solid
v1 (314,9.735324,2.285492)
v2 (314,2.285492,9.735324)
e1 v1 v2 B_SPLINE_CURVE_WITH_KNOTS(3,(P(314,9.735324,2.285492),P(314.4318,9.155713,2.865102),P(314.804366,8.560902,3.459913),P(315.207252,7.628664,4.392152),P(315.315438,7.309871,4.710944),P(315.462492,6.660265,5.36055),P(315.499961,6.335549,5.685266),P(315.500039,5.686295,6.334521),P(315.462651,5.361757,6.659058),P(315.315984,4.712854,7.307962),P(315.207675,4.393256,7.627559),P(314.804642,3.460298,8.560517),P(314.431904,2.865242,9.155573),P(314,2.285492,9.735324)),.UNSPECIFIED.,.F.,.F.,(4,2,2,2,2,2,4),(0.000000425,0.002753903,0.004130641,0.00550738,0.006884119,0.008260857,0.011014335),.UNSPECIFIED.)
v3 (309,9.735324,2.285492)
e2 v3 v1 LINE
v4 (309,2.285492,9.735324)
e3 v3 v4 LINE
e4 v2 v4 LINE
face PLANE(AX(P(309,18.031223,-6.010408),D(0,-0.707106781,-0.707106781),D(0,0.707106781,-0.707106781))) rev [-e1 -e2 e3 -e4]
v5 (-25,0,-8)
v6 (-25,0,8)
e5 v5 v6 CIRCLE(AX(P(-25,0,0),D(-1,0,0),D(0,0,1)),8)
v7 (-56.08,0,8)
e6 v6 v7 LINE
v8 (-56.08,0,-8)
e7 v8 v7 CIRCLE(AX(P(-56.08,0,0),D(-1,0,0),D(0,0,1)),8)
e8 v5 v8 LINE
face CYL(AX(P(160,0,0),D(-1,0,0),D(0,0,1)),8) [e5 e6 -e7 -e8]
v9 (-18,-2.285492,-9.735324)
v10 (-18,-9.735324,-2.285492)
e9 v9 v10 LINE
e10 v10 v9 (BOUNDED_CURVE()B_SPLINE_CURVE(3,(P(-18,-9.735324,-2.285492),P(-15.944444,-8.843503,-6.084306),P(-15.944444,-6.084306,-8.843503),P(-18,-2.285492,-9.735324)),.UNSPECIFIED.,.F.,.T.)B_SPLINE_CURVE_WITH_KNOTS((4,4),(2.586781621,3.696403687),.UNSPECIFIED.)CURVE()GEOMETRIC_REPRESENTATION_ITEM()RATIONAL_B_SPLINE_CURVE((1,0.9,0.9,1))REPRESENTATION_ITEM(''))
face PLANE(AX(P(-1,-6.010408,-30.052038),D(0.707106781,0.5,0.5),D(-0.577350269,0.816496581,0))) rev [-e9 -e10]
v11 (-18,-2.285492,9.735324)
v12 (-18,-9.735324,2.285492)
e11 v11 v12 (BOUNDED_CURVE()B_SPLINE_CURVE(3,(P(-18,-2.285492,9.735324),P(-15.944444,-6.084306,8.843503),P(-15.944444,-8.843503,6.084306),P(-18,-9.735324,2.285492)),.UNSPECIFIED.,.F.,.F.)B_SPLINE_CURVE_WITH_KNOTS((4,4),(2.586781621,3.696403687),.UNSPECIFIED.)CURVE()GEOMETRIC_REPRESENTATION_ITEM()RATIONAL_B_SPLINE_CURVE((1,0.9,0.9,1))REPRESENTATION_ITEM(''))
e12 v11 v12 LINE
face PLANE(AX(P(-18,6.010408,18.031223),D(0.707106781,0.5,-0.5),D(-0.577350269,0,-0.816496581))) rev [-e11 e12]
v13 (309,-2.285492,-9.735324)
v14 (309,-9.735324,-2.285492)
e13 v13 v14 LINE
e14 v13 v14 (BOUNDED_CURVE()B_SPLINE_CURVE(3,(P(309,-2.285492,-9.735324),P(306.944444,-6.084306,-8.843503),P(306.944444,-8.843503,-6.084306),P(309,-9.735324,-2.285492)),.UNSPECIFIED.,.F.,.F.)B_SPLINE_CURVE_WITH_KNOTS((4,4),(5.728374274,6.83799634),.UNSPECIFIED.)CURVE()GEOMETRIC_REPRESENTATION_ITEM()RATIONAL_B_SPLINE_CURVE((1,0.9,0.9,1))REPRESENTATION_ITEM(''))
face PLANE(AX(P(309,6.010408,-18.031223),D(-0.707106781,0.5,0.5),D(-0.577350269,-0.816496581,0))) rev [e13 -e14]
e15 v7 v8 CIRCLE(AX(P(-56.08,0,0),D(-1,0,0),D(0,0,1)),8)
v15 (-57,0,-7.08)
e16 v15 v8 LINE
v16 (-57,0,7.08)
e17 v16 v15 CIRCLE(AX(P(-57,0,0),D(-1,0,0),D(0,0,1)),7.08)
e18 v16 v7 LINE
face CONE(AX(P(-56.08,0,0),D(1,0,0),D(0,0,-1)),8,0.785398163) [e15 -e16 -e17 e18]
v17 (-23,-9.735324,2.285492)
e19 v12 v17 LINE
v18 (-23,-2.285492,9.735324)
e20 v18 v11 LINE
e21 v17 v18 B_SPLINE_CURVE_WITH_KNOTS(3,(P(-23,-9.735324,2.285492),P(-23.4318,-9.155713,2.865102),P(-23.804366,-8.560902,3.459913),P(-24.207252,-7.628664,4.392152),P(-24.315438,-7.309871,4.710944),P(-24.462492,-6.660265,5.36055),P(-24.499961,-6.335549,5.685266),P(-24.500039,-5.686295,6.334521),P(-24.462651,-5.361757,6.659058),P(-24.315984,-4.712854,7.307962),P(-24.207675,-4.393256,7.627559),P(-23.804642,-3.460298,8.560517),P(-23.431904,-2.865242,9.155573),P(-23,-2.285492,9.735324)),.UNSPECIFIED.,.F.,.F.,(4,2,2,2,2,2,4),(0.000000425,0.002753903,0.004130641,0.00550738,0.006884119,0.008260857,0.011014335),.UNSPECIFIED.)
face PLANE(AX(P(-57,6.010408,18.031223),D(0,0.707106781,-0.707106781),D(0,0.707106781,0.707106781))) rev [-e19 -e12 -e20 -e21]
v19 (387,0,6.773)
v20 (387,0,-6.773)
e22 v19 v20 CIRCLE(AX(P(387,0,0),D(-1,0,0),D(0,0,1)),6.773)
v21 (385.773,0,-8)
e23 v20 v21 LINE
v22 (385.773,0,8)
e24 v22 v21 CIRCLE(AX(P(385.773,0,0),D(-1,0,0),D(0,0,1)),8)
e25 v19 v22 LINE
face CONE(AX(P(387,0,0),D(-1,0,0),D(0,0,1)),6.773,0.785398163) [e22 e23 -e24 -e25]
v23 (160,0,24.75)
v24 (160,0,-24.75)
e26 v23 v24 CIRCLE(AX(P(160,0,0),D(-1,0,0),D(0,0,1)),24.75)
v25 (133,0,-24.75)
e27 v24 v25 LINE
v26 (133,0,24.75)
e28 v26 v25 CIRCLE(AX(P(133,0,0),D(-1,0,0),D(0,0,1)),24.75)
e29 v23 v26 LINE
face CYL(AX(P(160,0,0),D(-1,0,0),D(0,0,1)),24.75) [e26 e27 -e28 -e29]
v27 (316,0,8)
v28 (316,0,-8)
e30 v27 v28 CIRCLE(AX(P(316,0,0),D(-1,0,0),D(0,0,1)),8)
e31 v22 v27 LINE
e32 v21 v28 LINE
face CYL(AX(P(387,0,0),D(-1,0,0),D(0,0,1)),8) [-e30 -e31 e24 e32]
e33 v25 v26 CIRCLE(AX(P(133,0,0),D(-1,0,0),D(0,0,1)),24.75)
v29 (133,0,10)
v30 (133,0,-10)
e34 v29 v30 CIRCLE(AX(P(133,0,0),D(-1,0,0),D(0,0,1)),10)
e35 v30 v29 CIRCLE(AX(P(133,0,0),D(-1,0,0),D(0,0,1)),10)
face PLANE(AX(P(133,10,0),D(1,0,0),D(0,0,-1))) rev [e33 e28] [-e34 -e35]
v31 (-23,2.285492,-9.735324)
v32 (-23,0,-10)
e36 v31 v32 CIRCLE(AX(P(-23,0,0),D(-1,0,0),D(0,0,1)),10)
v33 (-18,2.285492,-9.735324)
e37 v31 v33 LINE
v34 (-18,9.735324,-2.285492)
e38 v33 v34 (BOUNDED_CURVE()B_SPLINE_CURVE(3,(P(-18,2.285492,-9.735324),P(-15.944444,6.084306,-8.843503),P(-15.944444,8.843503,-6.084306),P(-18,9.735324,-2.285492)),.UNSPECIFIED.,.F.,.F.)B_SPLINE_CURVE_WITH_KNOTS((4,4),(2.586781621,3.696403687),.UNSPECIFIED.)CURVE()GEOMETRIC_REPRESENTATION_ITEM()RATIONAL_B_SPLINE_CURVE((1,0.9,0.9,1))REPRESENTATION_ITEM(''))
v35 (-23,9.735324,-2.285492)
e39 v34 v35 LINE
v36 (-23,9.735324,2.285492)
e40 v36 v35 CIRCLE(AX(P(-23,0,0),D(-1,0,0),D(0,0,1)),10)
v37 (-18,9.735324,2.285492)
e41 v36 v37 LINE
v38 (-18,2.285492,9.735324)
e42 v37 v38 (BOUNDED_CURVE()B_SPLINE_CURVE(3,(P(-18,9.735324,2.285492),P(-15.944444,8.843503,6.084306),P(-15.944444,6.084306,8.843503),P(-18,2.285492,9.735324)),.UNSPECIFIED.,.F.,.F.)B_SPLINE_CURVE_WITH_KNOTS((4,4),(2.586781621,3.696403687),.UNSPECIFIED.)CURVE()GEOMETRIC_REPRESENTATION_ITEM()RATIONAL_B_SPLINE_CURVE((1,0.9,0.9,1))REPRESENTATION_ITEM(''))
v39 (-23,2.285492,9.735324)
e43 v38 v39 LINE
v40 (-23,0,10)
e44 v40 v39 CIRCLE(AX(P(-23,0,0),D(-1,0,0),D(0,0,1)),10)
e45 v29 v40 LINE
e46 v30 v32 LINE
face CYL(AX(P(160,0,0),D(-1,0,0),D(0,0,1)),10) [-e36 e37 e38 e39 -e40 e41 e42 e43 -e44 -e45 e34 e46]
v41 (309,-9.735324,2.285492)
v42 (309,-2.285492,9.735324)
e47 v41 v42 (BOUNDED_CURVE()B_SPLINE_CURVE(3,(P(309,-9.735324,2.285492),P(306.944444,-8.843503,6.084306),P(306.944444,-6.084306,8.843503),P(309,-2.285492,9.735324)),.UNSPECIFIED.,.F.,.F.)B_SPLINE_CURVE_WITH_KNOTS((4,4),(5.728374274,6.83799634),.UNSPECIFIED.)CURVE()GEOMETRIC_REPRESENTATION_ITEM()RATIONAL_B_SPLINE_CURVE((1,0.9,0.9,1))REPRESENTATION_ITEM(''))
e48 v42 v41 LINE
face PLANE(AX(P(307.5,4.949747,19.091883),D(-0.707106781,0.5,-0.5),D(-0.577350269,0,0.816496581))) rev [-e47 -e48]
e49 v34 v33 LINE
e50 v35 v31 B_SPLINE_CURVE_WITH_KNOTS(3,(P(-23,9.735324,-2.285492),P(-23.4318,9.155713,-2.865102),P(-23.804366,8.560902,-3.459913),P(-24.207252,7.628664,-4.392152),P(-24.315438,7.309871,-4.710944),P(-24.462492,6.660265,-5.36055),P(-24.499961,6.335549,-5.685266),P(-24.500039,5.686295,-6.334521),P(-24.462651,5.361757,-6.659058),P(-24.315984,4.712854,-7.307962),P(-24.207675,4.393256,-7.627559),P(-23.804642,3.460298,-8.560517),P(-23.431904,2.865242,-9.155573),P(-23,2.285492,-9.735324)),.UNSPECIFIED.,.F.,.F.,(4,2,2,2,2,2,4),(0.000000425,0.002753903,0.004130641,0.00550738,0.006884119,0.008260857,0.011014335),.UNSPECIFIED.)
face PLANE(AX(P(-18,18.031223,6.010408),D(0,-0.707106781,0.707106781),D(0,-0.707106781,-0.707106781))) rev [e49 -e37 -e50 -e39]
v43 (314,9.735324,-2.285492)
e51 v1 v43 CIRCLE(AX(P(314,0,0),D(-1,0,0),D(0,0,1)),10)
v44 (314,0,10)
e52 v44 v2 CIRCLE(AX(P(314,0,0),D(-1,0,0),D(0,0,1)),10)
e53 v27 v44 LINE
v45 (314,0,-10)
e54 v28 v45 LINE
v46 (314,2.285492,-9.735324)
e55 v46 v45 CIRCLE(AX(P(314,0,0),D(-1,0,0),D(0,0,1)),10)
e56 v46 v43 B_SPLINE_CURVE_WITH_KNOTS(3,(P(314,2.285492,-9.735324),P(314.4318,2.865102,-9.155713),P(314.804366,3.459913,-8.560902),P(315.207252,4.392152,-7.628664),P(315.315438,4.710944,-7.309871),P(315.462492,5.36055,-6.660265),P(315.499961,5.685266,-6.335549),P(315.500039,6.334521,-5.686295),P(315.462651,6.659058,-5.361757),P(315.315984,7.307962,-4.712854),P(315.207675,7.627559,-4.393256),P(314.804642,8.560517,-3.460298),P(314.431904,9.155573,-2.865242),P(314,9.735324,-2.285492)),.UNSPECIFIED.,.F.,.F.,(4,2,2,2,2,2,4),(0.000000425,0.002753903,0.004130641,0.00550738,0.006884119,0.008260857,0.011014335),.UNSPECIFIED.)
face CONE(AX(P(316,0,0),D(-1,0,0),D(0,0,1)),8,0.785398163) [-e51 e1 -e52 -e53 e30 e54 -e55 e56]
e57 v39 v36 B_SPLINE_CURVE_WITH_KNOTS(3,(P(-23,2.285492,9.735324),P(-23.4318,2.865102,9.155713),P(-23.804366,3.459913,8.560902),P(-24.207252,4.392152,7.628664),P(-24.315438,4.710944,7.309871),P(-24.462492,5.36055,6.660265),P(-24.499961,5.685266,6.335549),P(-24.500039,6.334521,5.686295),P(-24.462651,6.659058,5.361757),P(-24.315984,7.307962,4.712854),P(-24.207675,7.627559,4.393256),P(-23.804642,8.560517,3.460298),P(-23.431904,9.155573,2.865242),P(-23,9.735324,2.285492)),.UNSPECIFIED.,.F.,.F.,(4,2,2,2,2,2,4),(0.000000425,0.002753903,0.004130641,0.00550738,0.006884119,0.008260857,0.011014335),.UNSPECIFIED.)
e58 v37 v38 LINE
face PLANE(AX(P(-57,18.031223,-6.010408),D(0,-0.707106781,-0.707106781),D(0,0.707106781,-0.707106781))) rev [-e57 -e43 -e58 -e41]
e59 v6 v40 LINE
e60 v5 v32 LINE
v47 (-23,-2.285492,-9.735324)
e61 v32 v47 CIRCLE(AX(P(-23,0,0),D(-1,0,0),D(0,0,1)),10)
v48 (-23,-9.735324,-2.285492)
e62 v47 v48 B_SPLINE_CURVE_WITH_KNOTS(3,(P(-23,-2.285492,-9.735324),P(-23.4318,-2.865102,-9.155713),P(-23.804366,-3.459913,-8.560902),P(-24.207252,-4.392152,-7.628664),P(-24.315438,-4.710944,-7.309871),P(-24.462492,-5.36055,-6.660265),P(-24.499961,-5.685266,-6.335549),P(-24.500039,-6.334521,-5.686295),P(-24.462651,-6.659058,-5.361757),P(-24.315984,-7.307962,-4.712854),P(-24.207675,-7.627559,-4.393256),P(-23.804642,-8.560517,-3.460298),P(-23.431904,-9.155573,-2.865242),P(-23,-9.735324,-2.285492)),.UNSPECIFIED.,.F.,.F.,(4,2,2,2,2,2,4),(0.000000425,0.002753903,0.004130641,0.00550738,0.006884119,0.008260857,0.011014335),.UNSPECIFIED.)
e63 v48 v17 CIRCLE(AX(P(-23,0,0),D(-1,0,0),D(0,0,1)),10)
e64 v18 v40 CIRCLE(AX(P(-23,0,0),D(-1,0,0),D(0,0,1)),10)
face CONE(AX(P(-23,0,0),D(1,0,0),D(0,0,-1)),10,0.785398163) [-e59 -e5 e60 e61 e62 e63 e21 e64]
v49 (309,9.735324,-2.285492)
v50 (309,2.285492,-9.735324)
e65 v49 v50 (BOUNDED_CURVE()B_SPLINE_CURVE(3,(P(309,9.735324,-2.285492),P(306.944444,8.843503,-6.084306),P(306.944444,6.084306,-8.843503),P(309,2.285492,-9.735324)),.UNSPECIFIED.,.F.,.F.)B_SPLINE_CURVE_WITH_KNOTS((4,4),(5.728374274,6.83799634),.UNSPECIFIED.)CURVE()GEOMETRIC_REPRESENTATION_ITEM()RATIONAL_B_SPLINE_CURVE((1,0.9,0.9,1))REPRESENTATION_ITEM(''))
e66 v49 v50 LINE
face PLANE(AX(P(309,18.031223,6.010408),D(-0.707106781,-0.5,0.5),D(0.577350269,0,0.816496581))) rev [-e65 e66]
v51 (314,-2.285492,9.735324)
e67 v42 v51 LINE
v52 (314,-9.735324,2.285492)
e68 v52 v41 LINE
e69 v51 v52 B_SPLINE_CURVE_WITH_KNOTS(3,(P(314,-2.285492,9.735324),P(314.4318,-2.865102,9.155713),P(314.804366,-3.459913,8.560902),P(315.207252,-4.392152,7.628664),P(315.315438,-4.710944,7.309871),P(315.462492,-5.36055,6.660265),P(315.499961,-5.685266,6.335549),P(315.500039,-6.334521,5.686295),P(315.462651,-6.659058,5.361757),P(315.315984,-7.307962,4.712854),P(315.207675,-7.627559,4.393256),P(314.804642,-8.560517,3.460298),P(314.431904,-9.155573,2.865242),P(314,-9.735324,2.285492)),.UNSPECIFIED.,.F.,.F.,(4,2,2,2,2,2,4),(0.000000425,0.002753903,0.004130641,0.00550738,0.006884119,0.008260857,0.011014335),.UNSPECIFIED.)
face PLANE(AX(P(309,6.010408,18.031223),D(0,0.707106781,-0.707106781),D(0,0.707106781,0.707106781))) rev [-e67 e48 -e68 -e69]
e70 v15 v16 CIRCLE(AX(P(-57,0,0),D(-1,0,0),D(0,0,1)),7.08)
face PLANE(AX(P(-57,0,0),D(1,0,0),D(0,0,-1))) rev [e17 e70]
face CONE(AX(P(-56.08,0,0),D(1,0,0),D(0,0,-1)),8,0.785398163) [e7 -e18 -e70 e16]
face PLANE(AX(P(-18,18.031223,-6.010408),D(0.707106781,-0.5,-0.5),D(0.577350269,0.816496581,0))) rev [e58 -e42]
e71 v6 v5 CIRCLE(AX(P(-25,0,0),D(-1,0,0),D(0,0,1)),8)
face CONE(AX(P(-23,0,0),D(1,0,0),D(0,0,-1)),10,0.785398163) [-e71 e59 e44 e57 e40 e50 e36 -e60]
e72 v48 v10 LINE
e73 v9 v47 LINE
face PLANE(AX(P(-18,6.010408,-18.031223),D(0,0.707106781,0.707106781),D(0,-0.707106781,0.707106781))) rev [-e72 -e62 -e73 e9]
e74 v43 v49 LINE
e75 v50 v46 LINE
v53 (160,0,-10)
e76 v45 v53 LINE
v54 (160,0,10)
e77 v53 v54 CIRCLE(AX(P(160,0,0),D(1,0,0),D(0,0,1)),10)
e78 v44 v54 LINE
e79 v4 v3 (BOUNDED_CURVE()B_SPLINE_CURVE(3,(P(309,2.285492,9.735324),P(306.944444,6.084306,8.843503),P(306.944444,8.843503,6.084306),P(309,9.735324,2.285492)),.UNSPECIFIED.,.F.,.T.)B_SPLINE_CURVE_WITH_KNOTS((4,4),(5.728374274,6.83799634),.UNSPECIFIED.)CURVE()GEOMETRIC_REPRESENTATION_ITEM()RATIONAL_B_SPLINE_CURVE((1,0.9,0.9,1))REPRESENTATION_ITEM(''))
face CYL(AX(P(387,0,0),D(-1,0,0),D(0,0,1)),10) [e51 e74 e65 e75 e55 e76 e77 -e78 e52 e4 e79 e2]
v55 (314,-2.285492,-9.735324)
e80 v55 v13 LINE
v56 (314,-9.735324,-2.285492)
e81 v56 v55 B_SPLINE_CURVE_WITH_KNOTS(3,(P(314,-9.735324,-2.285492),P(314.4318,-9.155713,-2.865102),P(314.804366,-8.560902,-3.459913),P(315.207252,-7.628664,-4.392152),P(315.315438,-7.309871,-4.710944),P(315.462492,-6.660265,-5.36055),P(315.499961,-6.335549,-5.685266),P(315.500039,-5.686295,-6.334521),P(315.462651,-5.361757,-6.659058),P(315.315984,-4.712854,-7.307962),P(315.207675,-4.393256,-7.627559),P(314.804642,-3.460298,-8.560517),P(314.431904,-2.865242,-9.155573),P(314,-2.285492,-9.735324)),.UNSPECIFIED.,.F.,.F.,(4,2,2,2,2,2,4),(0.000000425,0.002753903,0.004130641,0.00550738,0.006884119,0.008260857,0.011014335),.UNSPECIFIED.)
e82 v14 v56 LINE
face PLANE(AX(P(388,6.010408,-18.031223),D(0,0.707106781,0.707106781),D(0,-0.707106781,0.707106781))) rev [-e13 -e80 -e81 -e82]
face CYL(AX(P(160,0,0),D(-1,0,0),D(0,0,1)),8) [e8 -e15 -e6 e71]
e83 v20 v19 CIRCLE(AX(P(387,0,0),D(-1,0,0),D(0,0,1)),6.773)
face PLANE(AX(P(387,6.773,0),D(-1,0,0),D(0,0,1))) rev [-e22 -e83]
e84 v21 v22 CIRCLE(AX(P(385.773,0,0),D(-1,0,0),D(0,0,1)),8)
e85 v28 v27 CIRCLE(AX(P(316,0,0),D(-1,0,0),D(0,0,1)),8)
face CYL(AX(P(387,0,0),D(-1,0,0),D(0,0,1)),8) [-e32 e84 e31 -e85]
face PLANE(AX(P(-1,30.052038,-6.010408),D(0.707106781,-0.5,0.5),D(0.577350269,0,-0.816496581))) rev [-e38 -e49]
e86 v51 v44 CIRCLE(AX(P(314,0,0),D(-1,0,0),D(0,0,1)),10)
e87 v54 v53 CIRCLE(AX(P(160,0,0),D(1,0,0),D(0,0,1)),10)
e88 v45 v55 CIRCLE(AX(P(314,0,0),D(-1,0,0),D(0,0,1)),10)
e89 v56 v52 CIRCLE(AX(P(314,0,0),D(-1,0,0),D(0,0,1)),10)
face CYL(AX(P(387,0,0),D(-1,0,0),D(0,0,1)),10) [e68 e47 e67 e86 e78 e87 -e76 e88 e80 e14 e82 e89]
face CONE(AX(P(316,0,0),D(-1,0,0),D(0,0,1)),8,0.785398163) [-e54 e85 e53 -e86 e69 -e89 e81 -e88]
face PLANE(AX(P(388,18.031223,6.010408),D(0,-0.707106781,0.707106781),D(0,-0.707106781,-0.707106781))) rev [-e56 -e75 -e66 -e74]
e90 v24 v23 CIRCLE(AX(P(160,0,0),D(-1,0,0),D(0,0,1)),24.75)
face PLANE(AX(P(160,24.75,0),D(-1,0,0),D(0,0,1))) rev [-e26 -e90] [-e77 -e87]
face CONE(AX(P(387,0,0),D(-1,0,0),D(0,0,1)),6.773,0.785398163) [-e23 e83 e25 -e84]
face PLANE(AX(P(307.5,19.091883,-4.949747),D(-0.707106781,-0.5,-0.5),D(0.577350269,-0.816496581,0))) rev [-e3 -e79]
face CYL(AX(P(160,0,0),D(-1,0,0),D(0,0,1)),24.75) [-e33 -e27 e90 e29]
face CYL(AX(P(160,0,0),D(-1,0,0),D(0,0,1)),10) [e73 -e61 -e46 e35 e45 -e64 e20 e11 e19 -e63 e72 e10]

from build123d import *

# Parameters (mm, degrees)
CUT_EXTRUDE1_DEPTH      = 17
CUT_EXTRUDE1_DEPTH_BACK = 17
CUT_EXTRUDE2_DEPTH      = 17
CUT_EXTRUDE2_DEPTH_BACK = 17
CUT_EXTRUDE3_DEPTH      = 17
CUT_EXTRUDE3_DEPTH_BACK = 17
CUT_EXTRUDE4_DEPTH      = 17
CUT_EXTRUDE4_DEPTH_BACK = 17


with BuildPart() as part:
    # Sketch1 → Revolve1 (revolve)
    with BuildSketch(Plane.XY, mode=Mode.PRIVATE) as revolve1_sk:
        Polygon((-57, 0), (-57, 7.08), (-56.08, 8), (-25, 8), (-23, 10), (133, 10), (133, 24.75), (160, 24.75), (160, 0), align=None)
    revolve(revolve1_sk.sketch.rotate(Axis((160, 0, 0), (-1, 0, 0)), 270), axis=Axis((160, 0, 0), (-1, 0, 0)))

    # Sketch2 → Cut-Extrude1 (cut, two sides: drawn at the far end of the back side and taken through both)
    with BuildSketch(Plane(origin=(0, 0, 0), x_dir=(1, 0, 0), z_dir=(0, -0.7071067811865475, 0.7071067811865476)).offset(-CUT_EXTRUDE1_DEPTH_BACK)):
        Polygon((-74, -25.5), (-1, -25.5), (-18, -8.5), (-57, -8.5), (-57, 8.5), (-18, 8.5), (-1, 25.5), (-74, 25.5), align=None)
    extrude(amount=CUT_EXTRUDE1_DEPTH + CUT_EXTRUDE1_DEPTH_BACK, mode=Mode.SUBTRACT)

    # Sketch3 → Cut-Extrude2 (cut, two sides: drawn at the far end of the back side and taken through both)
    with BuildSketch(Plane(origin=(0, 0, 0), x_dir=(-1, 0, 0), z_dir=(0, -0.7071067811865476, -0.7071067811865475)).offset(-CUT_EXTRUDE2_DEPTH_BACK)):
        Polygon((74, 25.5), (1, 25.5), (18, 8.5), (57, 8.5), (57, -8.5), (18, -8.5), (1, -25.5), (74, -25.5), align=None)
    extrude(amount=CUT_EXTRUDE2_DEPTH + CUT_EXTRUDE2_DEPTH_BACK, mode=Mode.SUBTRACT)

    # Sketch4 → Revolve2 (revolve)
    with BuildSketch(Plane.XY, mode=Mode.PRIVATE) as revolve2_sk:
        Polygon((119, 0), (119, 10), (314, 10), (316, 8), (385.773, 8), (387, 6.773), (387, 0), align=None)
    revolve(revolve2_sk.sketch.rotate(Axis((387, 0, 0), (-1, 0, 0)), 270), axis=Axis((387, 0, 0), (-1, 0, 0)))

    # Sketch5 → Cut-Extrude3 (cut, two sides: drawn at the far end of the back side and taken through both)
    with BuildSketch(Plane(origin=(0, 0, 0), x_dir=(1, 0, 0), z_dir=(0, -0.7071067811865475, 0.7071067811865476)).offset(-CUT_EXTRUDE3_DEPTH_BACK)):
        Polygon((307.5, -10), (307.5, -17), (392, -17), (392, 17), (307.5, 17), (307.5, 10), (309, 8.5), (388, 8.5), (388, -8.5), (309, -8.5), align=None)
    extrude(amount=CUT_EXTRUDE3_DEPTH + CUT_EXTRUDE3_DEPTH_BACK, mode=Mode.SUBTRACT)

    # Sketch6 → Cut-Extrude4 (cut, two sides: drawn at the far end of the back side and taken through both)
    with BuildSketch(Plane(origin=(0, 0, 0), x_dir=(-1, 0, 0), z_dir=(0, -0.7071067811865476, -0.7071067811865475)).offset(-CUT_EXTRUDE4_DEPTH_BACK)):
        Polygon((-307.5, 10), (-307.5, 17), (-392, 17), (-392, -17), (-307.5, -17), (-307.5, -10), (-309, -8.5), (-388, -8.5), (-388, 8.5), (-309, 8.5), align=None)
    extrude(amount=CUT_EXTRUDE4_DEPTH + CUT_EXTRUDE4_DEPTH_BACK, mode=Mode.SUBTRACT)


solid = part.part
